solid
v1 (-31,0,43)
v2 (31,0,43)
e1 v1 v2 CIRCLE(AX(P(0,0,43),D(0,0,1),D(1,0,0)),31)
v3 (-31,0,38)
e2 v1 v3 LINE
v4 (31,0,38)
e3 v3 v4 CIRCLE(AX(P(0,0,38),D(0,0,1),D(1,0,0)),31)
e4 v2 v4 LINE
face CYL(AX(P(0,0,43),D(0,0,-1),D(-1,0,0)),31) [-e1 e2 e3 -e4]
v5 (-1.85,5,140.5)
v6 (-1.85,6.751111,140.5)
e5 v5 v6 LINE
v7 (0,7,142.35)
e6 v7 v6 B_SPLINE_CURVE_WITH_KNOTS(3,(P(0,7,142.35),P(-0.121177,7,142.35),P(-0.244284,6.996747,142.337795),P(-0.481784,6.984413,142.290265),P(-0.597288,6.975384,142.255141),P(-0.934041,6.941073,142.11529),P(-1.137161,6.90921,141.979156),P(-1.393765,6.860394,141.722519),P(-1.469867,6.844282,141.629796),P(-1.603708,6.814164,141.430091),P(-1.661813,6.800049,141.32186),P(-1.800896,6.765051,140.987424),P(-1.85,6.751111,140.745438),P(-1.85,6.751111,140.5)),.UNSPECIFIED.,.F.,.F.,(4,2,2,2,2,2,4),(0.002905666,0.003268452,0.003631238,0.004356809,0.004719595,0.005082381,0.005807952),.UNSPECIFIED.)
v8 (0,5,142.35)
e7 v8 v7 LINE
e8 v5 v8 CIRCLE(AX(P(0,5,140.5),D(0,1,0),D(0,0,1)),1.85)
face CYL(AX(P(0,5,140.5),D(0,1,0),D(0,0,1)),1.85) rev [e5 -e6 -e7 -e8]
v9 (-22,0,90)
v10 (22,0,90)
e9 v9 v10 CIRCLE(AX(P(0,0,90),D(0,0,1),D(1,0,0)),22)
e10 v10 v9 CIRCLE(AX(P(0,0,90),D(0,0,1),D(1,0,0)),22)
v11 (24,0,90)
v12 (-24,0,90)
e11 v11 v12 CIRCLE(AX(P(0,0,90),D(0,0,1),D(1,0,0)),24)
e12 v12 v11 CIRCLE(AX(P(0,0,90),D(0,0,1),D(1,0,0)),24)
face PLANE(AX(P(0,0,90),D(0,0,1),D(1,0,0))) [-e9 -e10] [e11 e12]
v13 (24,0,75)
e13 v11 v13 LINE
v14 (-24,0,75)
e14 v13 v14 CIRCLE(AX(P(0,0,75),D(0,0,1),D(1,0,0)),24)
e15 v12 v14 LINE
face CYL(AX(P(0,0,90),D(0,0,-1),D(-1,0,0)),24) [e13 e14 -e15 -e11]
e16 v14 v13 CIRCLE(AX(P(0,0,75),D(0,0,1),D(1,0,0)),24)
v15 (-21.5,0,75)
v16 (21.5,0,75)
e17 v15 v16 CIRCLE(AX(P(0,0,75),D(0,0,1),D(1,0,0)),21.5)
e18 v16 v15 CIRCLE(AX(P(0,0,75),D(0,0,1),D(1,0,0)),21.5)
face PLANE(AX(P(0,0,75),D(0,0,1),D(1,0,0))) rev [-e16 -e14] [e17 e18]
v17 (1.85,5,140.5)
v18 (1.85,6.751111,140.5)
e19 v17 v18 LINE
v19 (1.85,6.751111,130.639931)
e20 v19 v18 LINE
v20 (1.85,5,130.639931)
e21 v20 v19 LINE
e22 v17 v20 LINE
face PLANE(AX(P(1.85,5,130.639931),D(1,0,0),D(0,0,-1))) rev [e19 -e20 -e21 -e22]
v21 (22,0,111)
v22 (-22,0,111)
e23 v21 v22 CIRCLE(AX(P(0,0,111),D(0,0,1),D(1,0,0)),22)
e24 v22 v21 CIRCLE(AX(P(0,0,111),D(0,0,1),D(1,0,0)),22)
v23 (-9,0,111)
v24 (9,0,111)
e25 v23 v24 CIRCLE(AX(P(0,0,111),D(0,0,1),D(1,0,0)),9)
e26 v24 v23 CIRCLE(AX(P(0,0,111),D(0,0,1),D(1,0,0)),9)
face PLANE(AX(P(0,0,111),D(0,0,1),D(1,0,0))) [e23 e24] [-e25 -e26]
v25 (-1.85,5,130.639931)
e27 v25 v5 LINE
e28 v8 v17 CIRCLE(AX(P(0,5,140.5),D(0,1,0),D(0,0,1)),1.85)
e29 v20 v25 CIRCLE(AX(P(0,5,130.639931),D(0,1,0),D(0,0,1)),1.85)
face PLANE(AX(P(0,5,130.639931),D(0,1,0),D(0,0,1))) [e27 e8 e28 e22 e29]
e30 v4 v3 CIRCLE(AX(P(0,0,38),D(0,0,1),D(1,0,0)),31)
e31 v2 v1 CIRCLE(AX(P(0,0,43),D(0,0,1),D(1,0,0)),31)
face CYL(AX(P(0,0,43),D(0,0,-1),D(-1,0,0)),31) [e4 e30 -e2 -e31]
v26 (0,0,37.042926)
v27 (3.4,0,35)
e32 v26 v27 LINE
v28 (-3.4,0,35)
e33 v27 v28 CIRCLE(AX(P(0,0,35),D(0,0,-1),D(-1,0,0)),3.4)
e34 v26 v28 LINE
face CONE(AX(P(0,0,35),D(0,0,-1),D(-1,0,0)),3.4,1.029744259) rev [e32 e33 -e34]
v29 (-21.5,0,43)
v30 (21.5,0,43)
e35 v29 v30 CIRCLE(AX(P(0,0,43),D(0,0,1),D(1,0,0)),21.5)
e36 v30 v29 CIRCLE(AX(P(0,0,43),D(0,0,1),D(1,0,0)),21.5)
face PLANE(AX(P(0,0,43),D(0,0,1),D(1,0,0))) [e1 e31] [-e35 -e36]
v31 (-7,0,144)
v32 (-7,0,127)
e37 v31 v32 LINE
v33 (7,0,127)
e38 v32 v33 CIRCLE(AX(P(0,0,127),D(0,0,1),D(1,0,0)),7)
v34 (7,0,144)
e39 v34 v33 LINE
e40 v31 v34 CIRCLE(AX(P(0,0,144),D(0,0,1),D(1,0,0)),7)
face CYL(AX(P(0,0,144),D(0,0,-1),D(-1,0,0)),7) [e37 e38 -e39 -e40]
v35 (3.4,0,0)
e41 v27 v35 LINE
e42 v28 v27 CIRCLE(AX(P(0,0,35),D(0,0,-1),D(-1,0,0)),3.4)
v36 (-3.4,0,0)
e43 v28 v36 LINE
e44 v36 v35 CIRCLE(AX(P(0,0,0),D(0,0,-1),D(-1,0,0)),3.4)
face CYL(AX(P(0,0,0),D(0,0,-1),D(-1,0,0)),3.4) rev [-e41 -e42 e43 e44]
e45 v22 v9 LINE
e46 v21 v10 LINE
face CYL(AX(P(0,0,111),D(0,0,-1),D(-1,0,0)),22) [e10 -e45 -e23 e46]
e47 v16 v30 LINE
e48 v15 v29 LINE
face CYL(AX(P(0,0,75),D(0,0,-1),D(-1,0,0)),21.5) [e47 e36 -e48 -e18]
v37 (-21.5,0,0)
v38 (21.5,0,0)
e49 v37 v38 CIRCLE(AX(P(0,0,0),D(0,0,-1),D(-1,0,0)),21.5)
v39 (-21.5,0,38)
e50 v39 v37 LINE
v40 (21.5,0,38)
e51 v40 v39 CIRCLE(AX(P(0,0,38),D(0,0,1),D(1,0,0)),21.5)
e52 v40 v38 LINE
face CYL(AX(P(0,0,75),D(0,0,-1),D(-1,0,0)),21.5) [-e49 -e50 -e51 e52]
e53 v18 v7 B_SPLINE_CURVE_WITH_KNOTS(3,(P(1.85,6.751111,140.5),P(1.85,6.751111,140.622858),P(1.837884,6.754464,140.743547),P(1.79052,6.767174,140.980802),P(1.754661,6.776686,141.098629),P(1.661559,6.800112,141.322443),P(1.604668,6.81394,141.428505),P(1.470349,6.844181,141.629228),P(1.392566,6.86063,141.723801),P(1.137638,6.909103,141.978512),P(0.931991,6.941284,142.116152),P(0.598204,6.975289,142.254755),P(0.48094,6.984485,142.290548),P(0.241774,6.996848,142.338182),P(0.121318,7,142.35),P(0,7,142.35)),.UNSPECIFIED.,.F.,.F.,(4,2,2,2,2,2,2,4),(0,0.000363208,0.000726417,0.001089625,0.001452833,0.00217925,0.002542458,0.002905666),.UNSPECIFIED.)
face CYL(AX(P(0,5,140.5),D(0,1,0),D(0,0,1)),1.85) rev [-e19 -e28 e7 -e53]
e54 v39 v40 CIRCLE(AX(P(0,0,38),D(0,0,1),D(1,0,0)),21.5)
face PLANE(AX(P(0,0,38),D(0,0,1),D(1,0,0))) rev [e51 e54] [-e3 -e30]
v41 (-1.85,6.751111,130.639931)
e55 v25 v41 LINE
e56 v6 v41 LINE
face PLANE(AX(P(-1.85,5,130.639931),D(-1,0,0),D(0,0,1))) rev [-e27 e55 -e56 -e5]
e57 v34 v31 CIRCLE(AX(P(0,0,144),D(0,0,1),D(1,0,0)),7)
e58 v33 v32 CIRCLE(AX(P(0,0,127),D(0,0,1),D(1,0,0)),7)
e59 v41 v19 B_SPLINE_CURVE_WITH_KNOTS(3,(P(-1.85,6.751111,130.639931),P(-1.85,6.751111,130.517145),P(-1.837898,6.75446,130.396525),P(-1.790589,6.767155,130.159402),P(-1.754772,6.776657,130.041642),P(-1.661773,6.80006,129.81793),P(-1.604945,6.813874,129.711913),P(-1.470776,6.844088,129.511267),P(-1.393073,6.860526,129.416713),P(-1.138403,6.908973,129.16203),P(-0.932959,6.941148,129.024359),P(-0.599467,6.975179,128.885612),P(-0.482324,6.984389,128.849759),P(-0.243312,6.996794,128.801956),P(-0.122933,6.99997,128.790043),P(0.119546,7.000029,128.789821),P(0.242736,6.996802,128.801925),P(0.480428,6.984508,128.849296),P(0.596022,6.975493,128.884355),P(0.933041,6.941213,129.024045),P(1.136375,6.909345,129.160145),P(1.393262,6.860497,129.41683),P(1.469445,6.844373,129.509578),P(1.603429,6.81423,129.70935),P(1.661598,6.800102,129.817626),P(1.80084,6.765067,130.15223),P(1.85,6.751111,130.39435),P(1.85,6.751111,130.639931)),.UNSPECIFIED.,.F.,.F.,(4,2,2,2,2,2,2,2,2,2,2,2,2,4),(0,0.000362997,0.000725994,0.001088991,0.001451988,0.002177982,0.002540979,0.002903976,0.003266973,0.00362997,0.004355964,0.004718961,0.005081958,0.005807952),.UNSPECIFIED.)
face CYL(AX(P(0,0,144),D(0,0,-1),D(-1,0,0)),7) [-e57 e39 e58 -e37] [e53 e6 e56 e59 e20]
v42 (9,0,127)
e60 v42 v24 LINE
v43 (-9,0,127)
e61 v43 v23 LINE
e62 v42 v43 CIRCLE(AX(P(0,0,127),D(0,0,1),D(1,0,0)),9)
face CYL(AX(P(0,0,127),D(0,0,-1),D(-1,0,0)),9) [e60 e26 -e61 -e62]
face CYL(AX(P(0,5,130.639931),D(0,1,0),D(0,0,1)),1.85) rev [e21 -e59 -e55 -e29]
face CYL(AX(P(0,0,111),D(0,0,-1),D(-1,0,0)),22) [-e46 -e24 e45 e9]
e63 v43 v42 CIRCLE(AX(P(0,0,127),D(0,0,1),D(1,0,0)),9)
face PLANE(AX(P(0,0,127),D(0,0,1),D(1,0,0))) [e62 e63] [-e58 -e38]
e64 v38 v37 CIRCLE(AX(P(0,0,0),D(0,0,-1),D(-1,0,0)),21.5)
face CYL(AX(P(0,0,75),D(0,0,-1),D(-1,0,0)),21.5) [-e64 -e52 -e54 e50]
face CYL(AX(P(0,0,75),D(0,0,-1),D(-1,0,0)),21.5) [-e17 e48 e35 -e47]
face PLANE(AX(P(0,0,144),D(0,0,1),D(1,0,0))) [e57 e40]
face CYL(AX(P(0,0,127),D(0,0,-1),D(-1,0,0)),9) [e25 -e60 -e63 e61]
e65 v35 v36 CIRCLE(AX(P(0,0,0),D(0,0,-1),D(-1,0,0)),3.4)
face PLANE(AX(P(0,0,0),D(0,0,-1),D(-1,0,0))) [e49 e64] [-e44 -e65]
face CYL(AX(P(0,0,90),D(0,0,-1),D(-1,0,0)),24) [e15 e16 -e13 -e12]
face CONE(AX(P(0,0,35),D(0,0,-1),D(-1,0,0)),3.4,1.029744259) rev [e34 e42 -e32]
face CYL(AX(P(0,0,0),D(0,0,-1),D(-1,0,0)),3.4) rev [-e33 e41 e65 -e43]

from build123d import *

# Parameters (mm, degrees)
SKETCH1_R             = 21.5
BOSS_EXTRUDE1_DEPTH   = 37
SKETCH2_R             = 24
BOSS_EXTRUDE2_DEPTH   = 15
SKETCH3_R             = 22
BOSS_EXTRUDE3_DEPTH   = 21
SKETCH4_R             = 9
BOSS_EXTRUDE4_DEPTH   = 16
SKETCH5_R             = 7
BOSS_EXTRUDE5_DEPTH   = 17
CUT_EXTRUDE1_START    = 30
CUT_EXTRUDE1_DEPTH    = 25
BOSS_EXTRUDE6_START   = 38
SKETCH7_R             = 21.5
BOSS_EXTRUDE6_DEPTH   = 38
SKETCH9_R             = 31
BOSS_EXTRUDE7_DEPTH   = 5
M8_TAPPED_HOLE1_D     = 6.8
M8_TAPPED_HOLE1_DEPTH = 35
M8_TAPPED_HOLE1_TIP   = 2.042926105


with BuildPart() as part:
    # Sketch1 → Boss-Extrude1 (new body)
    with BuildSketch(Plane.XY.offset(38)):
        Circle(SKETCH1_R)
    extrude(amount=BOSS_EXTRUDE1_DEPTH)

    # Sketch2 → Boss-Extrude2 (add)
    with BuildSketch(Plane.XY.offset(75)):
        Circle(SKETCH2_R)
    extrude(amount=BOSS_EXTRUDE2_DEPTH)

    # Sketch3 → Boss-Extrude3 (add)
    with BuildSketch(Plane.XY.offset(90)):
        Circle(SKETCH3_R)
    extrude(amount=BOSS_EXTRUDE3_DEPTH)

    # Sketch4 → Boss-Extrude4 (add)
    with BuildSketch(Plane.XY.offset(111)):
        Circle(SKETCH4_R)
    extrude(amount=BOSS_EXTRUDE4_DEPTH)

    # Sketch5 → Boss-Extrude5 (add)
    with BuildSketch(Plane.XY.offset(127)):
        Circle(SKETCH5_R)
    extrude(amount=BOSS_EXTRUDE5_DEPTH)

    # Sketch6 → Cut-Extrude1 (cut)
    with BuildSketch(Plane(origin=(0, 0, 0), x_dir=(1, 0, 0), z_dir=(0, 1, 0)).offset(CUT_EXTRUDE1_START)):
        with BuildLine():
            Line((1.85, -130.63993085), (1.85, -140.5))
            ThreePointArc((1.85, -140.5), (0, -142.35), (-1.85, -140.5))
            Line((-1.85, -140.5), (-1.85, -130.63993085))
            ThreePointArc((-1.85, -130.63993085), (0, -128.78993085), (1.85, -130.63993085))
        make_face()
    extrude(amount=-CUT_EXTRUDE1_DEPTH, mode=Mode.SUBTRACT)

    # Sketch7 → Boss-Extrude6 (add)
    with BuildSketch(Plane(origin=(0, 0, 38), x_dir=(-1, 0, 0), z_dir=(0, 0, -1)).offset(BOSS_EXTRUDE6_START)):
        Circle(SKETCH7_R)
    extrude(amount=-BOSS_EXTRUDE6_DEPTH)

    # Sketch9 → Boss-Extrude7 (add)
    with BuildSketch(Plane.XY.offset(38)):
        Circle(SKETCH9_R)
    extrude(amount=BOSS_EXTRUDE7_DEPTH)

    # M8 Tapped Hole1
    with Locations(Plane(origin=(0, 0, 0), x_dir=(-1, 0, 0), z_dir=(0, 0, -1))):
        with Locations((0, 0)):
            Hole(M8_TAPPED_HOLE1_D / 2, depth=M8_TAPPED_HOLE1_DEPTH)
            with Locations((0, 0, -(M8_TAPPED_HOLE1_DEPTH + M8_TAPPED_HOLE1_TIP / 2))):  # 118° drill point
                Cone(0, M8_TAPPED_HOLE1_D / 2, M8_TAPPED_HOLE1_TIP, mode=Mode.SUBTRACT)


solid = part.part
